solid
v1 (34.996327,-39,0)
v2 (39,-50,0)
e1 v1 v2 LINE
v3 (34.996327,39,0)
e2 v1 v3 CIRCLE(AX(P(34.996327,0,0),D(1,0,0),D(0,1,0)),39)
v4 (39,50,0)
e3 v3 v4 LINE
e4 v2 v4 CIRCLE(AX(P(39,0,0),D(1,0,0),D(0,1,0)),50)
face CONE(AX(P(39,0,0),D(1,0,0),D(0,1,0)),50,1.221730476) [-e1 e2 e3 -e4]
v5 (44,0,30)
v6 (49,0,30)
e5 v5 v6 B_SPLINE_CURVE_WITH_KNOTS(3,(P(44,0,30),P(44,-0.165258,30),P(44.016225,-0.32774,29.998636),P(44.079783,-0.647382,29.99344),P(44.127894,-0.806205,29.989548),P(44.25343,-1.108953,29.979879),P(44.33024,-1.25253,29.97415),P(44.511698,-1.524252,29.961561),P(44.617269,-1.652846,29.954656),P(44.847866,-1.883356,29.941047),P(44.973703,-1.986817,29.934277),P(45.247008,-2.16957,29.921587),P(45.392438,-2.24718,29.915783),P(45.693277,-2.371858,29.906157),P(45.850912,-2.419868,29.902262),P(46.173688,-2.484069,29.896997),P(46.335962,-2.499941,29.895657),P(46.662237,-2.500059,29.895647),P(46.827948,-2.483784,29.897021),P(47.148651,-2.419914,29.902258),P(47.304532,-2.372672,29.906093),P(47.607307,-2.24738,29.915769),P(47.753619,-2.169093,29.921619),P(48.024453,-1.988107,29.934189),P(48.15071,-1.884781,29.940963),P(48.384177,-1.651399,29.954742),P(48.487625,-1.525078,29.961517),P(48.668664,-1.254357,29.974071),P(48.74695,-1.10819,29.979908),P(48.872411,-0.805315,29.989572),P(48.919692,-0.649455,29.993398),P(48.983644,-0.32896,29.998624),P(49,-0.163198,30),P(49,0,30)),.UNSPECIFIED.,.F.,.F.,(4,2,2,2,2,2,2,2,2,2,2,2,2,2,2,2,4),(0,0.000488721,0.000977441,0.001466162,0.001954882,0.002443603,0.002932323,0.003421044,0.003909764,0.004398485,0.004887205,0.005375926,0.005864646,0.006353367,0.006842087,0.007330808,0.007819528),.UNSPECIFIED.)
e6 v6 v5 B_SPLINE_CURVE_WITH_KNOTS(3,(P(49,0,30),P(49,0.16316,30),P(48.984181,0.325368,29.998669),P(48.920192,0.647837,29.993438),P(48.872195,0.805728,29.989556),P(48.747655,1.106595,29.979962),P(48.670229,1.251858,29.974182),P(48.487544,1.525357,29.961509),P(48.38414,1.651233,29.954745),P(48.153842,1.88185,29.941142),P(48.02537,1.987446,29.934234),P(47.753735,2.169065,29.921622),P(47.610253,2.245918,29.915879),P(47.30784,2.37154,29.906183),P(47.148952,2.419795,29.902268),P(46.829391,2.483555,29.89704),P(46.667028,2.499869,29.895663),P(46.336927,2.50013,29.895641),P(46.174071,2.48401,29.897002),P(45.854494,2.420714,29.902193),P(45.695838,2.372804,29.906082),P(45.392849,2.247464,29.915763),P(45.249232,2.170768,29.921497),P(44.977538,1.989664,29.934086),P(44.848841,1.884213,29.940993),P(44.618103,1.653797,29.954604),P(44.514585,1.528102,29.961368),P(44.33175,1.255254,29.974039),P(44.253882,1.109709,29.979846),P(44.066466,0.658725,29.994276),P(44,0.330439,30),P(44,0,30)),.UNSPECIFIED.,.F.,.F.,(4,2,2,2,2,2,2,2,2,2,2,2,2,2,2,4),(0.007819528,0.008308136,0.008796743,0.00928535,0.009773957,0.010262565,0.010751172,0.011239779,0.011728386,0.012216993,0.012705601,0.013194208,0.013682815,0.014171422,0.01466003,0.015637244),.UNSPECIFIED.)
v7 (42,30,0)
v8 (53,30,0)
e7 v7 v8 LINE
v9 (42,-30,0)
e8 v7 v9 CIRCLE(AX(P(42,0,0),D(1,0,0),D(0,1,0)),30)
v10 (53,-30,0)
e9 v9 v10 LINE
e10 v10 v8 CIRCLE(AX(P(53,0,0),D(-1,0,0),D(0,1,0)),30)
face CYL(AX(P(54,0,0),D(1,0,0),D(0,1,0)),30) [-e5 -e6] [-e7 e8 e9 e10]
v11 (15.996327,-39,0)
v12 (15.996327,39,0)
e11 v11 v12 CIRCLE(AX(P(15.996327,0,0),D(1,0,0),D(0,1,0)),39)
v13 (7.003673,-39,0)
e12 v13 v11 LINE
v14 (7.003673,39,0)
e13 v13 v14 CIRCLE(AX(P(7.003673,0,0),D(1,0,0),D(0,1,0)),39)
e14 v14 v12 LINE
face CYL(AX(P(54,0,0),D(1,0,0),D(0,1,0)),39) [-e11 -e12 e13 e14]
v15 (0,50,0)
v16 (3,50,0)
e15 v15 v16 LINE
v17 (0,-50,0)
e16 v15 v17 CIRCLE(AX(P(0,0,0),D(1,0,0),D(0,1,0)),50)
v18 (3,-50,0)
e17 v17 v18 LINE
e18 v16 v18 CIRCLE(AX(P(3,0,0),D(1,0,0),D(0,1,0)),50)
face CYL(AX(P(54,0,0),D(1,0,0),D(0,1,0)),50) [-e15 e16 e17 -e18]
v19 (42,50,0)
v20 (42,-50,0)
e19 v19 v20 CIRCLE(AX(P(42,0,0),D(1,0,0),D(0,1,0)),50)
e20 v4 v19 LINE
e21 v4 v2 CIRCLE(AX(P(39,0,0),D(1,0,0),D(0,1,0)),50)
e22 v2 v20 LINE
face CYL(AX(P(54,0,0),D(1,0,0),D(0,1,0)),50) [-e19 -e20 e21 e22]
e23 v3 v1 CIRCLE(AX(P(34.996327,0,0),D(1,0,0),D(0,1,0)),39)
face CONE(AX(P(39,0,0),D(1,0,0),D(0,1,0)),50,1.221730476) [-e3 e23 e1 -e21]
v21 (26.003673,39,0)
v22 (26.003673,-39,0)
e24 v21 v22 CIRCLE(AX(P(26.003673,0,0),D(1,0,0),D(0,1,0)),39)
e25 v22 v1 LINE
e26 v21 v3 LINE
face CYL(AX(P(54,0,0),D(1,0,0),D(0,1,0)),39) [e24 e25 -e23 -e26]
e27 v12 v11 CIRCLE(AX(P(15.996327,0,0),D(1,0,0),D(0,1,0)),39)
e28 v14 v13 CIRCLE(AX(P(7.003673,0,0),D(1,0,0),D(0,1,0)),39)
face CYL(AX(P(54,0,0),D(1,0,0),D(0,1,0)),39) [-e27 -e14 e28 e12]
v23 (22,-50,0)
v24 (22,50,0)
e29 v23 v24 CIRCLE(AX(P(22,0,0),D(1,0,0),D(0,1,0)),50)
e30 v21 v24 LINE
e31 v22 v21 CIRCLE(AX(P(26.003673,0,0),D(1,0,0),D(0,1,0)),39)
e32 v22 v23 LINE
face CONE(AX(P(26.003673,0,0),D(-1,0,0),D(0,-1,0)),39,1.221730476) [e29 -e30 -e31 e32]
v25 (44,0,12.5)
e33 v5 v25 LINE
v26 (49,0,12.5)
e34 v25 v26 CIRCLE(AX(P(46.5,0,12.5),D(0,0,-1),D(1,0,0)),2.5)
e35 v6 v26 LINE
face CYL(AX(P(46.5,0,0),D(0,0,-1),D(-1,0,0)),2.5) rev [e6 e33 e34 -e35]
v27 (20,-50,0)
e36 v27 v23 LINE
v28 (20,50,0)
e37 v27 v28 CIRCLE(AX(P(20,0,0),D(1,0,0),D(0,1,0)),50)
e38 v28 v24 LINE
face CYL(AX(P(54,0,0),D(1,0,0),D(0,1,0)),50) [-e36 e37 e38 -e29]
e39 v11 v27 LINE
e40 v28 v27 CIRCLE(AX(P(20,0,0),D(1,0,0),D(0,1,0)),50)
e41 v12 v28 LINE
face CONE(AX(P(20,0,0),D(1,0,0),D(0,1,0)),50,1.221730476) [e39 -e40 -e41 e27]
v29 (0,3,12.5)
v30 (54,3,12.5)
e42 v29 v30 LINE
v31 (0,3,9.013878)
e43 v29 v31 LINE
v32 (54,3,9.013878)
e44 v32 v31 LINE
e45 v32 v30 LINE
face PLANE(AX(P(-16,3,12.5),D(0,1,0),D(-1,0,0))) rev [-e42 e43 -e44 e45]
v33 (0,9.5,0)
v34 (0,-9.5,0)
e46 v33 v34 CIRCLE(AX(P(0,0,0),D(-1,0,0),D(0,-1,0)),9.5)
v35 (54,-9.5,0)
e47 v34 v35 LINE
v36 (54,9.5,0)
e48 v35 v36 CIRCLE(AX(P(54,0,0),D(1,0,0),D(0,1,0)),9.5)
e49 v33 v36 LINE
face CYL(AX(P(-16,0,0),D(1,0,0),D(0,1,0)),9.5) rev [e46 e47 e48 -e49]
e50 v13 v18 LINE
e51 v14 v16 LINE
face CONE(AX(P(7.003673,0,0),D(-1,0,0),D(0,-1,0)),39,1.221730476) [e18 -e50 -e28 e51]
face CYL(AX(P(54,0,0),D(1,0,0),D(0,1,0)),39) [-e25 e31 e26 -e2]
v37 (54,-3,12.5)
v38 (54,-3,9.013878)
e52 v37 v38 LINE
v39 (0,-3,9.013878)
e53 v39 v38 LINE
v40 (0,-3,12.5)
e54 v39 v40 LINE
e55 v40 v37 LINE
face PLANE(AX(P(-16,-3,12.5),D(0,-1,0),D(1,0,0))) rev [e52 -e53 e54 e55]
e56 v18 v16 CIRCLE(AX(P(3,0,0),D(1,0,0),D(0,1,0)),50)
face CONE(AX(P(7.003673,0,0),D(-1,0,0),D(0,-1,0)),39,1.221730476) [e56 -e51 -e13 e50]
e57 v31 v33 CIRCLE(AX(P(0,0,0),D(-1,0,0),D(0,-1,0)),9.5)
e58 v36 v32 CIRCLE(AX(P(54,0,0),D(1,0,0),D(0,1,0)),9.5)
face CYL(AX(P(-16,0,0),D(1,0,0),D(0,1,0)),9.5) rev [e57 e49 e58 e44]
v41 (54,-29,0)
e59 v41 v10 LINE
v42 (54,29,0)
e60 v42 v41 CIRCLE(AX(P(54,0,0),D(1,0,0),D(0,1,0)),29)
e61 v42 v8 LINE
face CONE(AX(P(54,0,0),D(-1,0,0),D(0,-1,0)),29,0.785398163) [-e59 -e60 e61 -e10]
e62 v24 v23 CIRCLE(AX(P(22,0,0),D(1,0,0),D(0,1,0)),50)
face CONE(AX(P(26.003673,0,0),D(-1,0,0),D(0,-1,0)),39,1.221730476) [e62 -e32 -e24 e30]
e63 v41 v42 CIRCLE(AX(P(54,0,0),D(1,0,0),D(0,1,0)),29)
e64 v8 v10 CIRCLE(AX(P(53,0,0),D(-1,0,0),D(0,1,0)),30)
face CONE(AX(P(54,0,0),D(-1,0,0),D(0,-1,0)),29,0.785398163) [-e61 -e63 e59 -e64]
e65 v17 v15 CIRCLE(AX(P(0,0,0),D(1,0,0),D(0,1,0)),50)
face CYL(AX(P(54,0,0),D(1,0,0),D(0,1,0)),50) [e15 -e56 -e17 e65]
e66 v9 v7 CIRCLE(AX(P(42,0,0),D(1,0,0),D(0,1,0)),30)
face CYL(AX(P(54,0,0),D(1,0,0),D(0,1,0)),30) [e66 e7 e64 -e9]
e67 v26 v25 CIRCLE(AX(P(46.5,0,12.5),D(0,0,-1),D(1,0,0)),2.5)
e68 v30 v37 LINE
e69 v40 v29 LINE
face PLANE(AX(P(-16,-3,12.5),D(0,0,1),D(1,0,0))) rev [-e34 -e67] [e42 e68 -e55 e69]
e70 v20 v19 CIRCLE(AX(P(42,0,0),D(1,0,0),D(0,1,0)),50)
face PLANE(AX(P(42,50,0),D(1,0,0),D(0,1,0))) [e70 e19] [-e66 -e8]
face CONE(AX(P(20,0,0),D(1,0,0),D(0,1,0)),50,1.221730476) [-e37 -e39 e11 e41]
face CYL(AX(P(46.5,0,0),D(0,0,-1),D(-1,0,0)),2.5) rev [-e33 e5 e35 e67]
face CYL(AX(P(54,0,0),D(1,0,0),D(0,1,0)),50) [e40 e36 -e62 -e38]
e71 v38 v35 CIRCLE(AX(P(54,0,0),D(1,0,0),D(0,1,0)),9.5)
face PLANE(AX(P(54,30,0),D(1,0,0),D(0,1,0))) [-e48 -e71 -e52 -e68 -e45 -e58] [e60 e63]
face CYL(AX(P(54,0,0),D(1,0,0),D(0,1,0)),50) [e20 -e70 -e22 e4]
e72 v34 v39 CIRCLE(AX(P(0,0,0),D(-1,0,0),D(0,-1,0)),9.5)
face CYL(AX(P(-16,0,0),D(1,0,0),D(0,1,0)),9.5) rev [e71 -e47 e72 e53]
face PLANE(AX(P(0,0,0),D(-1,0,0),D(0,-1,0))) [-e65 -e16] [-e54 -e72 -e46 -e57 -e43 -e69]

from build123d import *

# Parameters (mm, degrees)
SKETCH2_R          = 9.5
CUT_EXTRUDE1_DEPTH = 70
CHAMFER1_SIZE      = 1
SKETCH7_W          = 6
SKETCH7_H          = 6
CUT_EXTRUDE2_DEPTH = 70


with BuildPart() as part:
    # Sketch1 → Revolve1 (revolve)
    with BuildSketch(Plane.XY):
        Polygon((0, 0), (0, 50), (3, 50), (7.003672577, 39), (15.996327423, 39), (20, 50), (22, 50), (26.003672577, 39), (34.996327423, 39), (39, 50), (42, 50), (42, 30), (54, 30), (54, 0), align=None)
    revolve(axis=Axis((54, 0, 0), (-1, 0, 0)))

    # Sketch2 → Cut-Extrude1 (cut)
    with BuildSketch(Plane(origin=(54, 0, 0), x_dir=(0, 0, -1), z_dir=(1, 0, 0))):
        with Locations(Location((0, 0, 0), (0, 0, 90))):
            Circle(SKETCH2_R)
    extrude(amount=-CUT_EXTRUDE1_DEPTH, mode=Mode.SUBTRACT)

    # Sketch5 → M6 Tapped Hole1 (revolve, cut)
    with BuildSketch(Plane.YZ.offset(46.5)):
        Polygon((0, 0), (0, 51.502151548), (2.5, 50), (2.5, 0), align=None)
    revolve(axis=Axis((46.5, 0, -6.35), (0, 0, 1)), mode=Mode.SUBTRACT)

    # Chamfer1
    chamfer1_edges = [part.edges().sort_by_distance(p)[0] for p in [
        (54, -30, 0),
    ]]
    chamfer(chamfer1_edges, length=CHAMFER1_SIZE)

    # Sketch7 → Cut-Extrude2 (cut)
    with BuildSketch(Plane(origin=(54, 0, 0), x_dir=(0, 0, -1), z_dir=(1, 0, 0))):
        with Locations((-9.5, 0)):
            Rectangle(SKETCH7_W, SKETCH7_H)
    extrude(amount=-CUT_EXTRUDE2_DEPTH, mode=Mode.SUBTRACT)


solid = part.part
